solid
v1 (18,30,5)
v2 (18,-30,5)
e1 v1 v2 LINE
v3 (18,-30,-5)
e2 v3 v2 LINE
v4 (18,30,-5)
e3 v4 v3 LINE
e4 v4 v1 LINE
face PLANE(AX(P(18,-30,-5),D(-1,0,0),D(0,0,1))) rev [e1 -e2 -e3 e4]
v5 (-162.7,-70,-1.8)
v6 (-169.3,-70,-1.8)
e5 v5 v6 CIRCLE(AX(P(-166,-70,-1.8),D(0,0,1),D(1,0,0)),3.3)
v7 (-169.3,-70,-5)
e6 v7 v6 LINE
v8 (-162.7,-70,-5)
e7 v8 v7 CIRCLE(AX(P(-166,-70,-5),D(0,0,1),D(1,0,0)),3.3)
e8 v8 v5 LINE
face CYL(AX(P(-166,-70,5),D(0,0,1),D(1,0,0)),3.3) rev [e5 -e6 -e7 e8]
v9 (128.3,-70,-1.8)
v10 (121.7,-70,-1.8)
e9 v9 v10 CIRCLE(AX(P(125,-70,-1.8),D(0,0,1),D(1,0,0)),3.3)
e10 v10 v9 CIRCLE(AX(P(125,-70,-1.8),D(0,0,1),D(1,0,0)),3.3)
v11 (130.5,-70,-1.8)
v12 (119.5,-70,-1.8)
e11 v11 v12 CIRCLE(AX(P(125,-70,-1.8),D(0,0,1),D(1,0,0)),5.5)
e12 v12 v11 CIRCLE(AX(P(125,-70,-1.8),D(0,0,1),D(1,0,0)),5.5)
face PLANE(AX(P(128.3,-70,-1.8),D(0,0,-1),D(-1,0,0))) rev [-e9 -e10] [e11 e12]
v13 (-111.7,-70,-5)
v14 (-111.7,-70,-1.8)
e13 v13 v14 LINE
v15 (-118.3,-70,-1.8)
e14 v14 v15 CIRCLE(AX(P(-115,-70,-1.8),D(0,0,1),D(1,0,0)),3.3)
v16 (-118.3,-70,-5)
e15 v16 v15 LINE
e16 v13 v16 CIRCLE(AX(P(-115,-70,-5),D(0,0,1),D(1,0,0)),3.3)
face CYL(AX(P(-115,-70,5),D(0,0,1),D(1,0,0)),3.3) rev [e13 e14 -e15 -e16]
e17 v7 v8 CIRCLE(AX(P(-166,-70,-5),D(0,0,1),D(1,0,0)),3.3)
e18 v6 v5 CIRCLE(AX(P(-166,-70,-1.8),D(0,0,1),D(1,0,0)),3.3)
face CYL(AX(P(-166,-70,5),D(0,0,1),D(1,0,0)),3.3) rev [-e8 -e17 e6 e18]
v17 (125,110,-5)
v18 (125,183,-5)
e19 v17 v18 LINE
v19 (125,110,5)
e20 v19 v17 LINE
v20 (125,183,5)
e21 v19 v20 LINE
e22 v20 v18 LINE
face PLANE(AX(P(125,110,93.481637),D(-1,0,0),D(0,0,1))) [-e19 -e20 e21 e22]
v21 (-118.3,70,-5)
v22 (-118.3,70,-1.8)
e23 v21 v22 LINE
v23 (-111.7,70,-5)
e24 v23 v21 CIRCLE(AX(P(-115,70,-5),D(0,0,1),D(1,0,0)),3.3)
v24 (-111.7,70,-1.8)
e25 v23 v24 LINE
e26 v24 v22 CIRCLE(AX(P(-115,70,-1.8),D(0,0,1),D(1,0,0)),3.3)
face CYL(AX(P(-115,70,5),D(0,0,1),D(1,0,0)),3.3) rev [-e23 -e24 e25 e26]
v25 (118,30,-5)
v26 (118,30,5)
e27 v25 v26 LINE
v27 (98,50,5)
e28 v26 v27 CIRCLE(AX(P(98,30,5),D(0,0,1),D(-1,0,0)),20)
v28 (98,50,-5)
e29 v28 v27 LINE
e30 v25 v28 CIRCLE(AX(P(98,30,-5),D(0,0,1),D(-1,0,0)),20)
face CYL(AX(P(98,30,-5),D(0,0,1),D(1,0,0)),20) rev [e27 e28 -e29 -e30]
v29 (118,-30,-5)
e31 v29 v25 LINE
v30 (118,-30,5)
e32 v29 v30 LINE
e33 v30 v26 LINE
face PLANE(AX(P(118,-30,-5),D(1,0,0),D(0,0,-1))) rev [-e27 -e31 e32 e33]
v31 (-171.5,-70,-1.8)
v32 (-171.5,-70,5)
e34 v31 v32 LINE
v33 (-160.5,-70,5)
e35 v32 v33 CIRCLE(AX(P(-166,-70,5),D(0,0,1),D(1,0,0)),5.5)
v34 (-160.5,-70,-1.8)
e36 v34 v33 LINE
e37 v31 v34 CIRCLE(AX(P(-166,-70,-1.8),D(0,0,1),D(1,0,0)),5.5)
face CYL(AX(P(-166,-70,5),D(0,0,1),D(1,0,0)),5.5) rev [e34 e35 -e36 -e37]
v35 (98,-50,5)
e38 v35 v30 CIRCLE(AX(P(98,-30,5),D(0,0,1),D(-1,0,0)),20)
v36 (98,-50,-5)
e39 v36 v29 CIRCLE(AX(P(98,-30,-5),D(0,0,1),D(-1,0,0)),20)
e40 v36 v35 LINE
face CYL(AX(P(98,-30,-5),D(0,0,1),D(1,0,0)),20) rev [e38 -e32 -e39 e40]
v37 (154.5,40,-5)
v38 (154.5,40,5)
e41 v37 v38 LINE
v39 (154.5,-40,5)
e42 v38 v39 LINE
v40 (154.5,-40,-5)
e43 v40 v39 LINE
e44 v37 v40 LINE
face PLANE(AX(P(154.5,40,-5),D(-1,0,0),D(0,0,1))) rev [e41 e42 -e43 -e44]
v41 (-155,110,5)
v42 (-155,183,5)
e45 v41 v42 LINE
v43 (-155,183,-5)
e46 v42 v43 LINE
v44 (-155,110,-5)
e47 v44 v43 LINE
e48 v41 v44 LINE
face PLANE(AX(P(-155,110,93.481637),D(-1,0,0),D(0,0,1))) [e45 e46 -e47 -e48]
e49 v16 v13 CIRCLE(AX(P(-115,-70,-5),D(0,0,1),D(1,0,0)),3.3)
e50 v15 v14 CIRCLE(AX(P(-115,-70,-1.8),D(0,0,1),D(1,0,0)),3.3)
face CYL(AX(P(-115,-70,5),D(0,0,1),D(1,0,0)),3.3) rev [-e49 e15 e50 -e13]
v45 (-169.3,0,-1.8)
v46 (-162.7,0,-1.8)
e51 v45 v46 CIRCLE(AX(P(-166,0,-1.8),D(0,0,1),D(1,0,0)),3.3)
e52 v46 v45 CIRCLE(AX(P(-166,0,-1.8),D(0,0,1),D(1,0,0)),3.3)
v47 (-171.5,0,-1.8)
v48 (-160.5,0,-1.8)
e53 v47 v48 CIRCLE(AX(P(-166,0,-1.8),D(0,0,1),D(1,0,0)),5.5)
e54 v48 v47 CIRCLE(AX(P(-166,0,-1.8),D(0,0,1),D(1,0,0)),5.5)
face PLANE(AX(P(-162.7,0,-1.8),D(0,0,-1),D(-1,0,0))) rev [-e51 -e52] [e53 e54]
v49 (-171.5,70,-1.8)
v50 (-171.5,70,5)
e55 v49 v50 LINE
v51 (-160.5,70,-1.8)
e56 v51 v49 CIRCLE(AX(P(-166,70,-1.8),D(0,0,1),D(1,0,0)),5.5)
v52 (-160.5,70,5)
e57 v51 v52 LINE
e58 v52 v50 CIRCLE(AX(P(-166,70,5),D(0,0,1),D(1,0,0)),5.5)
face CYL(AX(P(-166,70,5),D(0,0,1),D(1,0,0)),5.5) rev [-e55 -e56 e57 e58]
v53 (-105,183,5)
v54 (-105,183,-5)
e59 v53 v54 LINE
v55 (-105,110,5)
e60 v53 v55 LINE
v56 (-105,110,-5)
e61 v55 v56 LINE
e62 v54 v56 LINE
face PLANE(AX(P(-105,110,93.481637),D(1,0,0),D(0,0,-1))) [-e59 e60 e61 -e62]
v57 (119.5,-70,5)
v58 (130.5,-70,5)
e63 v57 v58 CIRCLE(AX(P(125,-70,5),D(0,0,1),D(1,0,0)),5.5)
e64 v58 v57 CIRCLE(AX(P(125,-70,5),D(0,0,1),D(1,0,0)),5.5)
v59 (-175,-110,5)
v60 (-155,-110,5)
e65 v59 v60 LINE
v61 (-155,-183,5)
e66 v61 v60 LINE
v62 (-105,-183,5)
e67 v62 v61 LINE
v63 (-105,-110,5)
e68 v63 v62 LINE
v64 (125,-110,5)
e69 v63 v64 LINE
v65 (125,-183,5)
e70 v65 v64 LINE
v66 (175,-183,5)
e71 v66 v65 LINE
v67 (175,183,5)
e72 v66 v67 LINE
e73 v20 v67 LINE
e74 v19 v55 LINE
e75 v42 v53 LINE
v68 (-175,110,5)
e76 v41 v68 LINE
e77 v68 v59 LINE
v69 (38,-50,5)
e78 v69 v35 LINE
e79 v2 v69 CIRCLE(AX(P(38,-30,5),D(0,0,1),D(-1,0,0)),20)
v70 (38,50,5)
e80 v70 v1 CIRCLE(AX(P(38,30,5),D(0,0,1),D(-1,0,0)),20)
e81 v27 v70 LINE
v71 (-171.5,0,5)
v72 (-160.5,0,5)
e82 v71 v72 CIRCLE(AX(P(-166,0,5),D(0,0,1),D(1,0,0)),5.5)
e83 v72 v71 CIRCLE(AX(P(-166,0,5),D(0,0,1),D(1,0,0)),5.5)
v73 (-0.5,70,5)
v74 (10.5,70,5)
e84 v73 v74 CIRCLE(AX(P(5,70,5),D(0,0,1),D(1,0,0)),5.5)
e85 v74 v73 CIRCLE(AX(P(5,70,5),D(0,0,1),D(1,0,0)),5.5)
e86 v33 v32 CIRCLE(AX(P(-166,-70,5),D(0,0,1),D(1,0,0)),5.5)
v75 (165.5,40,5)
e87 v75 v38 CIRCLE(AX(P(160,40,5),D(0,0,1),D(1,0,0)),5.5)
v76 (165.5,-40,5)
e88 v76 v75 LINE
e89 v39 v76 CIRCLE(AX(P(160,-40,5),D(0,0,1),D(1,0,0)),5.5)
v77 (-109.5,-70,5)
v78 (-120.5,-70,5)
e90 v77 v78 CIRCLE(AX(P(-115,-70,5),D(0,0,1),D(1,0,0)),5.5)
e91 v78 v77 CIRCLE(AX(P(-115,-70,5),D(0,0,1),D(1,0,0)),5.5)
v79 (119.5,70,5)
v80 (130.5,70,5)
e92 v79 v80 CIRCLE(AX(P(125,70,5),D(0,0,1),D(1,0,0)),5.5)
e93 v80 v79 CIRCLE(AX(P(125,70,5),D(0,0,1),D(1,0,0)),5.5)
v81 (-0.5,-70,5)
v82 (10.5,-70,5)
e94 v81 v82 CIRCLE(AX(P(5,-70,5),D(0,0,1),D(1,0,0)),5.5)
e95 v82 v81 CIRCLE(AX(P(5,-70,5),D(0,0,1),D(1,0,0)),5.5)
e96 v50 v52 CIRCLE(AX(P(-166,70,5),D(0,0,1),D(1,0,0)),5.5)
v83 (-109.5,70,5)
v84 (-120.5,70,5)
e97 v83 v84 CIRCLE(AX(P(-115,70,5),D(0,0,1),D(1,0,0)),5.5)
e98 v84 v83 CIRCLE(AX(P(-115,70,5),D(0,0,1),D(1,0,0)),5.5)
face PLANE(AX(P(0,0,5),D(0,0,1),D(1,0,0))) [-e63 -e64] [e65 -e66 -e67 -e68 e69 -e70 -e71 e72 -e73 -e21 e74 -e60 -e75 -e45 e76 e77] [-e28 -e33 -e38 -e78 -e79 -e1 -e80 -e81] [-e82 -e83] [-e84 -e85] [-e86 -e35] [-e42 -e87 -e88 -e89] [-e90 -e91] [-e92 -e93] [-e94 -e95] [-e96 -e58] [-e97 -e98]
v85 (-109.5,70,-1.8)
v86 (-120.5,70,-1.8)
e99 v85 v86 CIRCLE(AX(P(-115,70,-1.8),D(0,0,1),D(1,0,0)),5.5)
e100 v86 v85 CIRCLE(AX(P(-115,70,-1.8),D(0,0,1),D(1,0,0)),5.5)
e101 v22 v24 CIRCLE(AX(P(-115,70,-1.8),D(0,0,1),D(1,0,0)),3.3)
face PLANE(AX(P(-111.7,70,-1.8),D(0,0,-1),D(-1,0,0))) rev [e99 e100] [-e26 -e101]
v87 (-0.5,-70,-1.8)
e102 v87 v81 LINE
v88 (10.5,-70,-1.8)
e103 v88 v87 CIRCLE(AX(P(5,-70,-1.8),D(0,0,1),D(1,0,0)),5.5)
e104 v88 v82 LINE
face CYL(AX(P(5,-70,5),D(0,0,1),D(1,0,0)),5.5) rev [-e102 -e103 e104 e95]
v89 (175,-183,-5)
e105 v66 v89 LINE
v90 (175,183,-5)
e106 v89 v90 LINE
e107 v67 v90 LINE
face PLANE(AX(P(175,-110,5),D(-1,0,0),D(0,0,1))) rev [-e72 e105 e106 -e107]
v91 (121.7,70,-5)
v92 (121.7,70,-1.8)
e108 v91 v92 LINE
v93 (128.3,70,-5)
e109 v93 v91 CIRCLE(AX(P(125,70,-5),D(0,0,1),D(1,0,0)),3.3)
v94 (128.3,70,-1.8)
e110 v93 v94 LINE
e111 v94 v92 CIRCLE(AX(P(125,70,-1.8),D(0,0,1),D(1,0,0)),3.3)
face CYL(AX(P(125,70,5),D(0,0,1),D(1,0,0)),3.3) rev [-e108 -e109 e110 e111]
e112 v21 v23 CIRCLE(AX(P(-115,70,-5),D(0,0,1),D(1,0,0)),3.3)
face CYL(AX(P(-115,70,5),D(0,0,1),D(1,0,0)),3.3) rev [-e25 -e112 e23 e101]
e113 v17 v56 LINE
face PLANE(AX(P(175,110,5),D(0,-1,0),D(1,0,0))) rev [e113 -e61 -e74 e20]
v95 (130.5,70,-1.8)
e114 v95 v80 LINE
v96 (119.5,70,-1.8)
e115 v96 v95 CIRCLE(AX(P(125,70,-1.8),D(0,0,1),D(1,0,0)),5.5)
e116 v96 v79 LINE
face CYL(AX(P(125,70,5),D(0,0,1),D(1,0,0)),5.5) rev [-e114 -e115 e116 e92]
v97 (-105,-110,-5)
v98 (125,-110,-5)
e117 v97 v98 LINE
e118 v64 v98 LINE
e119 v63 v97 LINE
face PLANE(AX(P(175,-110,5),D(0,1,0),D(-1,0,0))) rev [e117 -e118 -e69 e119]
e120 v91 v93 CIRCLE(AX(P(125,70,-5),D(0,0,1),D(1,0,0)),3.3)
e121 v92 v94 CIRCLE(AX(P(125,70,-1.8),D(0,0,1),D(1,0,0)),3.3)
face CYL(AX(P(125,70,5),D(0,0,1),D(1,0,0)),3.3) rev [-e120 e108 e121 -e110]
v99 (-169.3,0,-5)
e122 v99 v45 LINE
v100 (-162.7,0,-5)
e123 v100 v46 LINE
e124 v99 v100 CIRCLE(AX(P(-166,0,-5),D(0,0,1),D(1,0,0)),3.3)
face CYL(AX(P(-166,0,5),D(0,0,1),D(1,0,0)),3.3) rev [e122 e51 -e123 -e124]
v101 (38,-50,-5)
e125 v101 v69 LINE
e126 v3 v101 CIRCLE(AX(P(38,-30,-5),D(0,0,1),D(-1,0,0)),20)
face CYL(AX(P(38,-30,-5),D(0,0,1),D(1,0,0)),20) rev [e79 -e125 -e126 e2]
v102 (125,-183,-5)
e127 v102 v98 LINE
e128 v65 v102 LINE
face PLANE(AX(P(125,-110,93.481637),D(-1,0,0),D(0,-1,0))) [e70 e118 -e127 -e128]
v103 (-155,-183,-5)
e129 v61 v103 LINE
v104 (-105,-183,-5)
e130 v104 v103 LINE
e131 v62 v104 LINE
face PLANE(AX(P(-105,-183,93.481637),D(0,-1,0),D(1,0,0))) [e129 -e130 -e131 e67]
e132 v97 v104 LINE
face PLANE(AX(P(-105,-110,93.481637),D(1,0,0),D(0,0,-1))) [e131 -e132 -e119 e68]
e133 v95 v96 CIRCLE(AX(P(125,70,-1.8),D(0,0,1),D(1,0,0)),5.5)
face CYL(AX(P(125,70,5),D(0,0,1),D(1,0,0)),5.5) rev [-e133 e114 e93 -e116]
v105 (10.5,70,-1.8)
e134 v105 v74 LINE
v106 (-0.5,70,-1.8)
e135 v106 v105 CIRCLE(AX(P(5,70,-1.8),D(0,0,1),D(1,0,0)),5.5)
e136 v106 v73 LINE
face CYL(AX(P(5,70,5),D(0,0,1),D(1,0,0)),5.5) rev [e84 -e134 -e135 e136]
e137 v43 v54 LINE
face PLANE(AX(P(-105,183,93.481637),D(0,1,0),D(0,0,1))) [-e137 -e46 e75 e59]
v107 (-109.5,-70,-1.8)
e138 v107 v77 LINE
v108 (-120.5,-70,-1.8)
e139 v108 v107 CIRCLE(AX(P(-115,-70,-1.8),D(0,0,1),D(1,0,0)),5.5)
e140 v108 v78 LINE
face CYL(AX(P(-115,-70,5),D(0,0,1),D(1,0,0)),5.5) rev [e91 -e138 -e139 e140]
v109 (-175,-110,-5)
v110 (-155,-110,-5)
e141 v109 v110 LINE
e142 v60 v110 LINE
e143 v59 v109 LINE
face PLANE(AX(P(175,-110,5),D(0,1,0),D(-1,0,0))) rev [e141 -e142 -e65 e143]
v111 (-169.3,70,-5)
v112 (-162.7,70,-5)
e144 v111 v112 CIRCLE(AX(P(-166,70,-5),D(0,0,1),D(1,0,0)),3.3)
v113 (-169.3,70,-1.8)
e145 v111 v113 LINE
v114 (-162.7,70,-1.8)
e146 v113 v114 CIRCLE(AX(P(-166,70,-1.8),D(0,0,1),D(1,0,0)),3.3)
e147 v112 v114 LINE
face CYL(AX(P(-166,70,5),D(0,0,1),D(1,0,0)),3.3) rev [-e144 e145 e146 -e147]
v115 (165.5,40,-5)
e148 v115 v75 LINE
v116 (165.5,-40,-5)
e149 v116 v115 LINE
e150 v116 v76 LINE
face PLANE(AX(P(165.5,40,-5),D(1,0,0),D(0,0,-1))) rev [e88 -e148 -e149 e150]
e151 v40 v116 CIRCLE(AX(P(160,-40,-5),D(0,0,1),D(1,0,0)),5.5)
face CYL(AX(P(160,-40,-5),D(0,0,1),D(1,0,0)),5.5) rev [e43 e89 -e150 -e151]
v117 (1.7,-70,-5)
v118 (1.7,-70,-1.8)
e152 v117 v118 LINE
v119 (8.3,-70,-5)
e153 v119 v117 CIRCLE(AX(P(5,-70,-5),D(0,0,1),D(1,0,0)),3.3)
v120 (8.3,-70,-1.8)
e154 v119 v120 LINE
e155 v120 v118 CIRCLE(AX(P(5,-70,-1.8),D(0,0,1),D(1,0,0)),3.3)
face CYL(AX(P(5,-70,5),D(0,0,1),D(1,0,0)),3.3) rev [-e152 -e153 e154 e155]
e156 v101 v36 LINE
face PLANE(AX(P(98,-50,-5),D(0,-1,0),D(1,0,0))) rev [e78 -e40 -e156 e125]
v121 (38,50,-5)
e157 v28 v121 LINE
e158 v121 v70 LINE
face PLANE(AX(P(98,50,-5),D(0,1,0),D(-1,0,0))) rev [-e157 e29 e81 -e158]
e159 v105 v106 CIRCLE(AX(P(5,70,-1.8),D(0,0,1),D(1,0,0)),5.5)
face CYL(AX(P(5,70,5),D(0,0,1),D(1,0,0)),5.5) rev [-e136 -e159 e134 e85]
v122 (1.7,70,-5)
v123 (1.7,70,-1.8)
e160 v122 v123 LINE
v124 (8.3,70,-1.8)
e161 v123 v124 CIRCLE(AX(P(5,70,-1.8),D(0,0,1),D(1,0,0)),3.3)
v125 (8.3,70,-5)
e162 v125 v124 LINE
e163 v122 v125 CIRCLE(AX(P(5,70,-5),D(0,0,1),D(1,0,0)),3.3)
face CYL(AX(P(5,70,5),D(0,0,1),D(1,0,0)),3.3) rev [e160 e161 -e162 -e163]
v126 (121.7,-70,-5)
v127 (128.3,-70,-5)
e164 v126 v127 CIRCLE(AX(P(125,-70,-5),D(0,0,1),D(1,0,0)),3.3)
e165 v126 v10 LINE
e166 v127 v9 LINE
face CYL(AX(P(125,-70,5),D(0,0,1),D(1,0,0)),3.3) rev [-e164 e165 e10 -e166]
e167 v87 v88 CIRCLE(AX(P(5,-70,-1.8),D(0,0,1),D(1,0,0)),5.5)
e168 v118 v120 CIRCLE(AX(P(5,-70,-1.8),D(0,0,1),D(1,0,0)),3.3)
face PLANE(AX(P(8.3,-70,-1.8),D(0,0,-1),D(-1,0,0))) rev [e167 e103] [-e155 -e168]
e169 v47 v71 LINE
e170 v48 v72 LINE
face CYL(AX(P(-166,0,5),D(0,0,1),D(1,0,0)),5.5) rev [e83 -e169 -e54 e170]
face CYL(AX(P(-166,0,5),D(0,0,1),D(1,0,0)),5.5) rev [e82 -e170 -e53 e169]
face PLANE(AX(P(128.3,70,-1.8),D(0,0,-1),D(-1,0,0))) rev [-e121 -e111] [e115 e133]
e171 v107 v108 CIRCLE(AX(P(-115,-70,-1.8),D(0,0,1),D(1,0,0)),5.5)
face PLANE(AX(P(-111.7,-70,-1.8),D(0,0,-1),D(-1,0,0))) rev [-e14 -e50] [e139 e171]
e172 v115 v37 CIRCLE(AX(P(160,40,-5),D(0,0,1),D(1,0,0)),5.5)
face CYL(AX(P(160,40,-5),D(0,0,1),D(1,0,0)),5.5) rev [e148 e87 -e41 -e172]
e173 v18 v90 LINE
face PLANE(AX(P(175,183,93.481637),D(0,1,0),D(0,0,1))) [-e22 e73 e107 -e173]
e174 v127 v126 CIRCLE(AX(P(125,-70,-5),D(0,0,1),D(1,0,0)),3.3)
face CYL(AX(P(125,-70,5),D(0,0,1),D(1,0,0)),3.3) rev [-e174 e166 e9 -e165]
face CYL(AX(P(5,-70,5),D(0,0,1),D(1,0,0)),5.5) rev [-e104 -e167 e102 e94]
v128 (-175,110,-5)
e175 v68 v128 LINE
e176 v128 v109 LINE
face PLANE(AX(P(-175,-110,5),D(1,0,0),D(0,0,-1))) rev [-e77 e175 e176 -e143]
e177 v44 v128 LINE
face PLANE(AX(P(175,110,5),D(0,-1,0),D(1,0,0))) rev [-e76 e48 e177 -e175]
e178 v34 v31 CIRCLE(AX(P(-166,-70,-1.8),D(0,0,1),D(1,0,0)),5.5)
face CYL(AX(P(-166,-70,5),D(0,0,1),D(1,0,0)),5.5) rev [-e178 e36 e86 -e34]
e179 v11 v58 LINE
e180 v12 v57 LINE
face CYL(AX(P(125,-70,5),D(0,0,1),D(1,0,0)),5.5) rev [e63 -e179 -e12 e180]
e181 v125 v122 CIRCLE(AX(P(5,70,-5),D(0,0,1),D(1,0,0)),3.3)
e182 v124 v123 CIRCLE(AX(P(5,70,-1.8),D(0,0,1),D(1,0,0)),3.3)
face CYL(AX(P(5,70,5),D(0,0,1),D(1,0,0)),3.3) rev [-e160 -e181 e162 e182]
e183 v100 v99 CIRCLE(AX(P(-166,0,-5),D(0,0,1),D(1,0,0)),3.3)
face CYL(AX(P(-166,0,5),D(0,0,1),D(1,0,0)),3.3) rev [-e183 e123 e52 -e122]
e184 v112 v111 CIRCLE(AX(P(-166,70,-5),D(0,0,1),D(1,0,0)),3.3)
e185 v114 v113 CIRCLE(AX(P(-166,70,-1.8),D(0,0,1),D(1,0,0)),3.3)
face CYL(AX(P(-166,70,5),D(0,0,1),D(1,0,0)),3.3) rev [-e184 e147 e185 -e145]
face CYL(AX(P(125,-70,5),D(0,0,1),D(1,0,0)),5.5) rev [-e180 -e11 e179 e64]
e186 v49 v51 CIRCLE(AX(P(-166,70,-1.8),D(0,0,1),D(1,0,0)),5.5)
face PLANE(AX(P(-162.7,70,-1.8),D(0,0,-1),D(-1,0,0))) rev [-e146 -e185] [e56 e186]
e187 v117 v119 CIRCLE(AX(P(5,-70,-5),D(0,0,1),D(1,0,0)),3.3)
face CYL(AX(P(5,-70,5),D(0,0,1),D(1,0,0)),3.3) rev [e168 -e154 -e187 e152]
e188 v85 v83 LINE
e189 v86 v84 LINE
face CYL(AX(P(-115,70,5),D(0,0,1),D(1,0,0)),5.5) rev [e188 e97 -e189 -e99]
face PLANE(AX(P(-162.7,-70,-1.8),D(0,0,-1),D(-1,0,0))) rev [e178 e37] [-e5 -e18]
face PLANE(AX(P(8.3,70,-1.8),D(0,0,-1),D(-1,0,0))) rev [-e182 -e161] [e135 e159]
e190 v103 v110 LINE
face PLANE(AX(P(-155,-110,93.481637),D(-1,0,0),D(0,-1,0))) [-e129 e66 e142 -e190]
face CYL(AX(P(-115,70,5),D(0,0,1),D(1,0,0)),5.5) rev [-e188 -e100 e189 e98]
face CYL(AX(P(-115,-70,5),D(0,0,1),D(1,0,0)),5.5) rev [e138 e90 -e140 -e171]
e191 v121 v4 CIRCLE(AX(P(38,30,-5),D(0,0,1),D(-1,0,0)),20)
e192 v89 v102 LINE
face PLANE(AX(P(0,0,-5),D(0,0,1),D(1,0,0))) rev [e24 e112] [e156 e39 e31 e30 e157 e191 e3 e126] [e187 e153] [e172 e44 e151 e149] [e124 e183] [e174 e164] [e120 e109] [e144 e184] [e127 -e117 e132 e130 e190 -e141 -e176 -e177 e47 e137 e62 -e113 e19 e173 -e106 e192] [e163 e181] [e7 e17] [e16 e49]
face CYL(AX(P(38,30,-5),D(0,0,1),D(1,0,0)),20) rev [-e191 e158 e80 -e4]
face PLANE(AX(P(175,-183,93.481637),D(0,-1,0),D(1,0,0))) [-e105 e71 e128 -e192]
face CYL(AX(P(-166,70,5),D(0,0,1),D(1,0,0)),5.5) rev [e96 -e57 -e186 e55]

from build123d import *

# Parameters (mm, degrees)
SKETCH_1_W                = 350
SKETCH_1_H                = 220
EXTRUDE_1_DEPTH           = 5
CUT_EXTRUDE_1_DEPTH       = 207.942020866
CUT_EXTRUDE_2_DEPTH       = 207.942020866
HOLE_WIZARD_1_D           = 6.6
HOLE_WIZARD_1_DEPTH       = 15
HOLE_WIZARD_1_CBORE_D     = 11
HOLE_WIZARD_1_CBORE_DEPTH = 6.8
HOLE_WIZARD_1_TIP         = 1.982840043
SKETCH_8_W                = 50
SKETCH_8_H                = 73
EXTRUDE_2_DEPTH           = 10
PATTERN_LINEAR_1_COUNT    = 2
PATTERN_LINEAR_1_PITCH    = 280


with BuildPart() as part:
    # 草图1 → 凸台-拉伸1 (new, symmetric)
    with BuildSketch(Plane.XY):
        Rectangle(SKETCH_1_W, SKETCH_1_H)
    extrude(amount=EXTRUDE_1_DEPTH, both=True)

    # 草图2 → 切除-拉伸1 (cut, through all)
    with BuildSketch(Plane.XY.offset(5)):
        with BuildLine():
            Line((-208, 40), (-208, -40))
            ThreePointArc((-208, -40), (-213.5, -45.5), (-219, -40))
            Line((-219, -40), (-219, 40))
            ThreePointArc((-219, 40), (-213.5, 45.5), (-208, 40))
        make_face()
        with BuildLine():
            Line((165.5, 40), (165.5, -40))
            ThreePointArc((165.5, -40), (160, -45.5), (154.5, -40))
            Line((154.5, -40), (154.5, 40))
            ThreePointArc((154.5, 40), (160, 45.5), (165.5, 40))
        make_face()
    extrude(amount=-CUT_EXTRUDE_1_DEPTH, mode=Mode.SUBTRACT)

    # 草图6 → 切除-拉伸2 (cut, through all)
    with BuildSketch(Plane.XY.offset(5)):
        with BuildLine():
            Line((98, -50), (38, -50))
            ThreePointArc((38, -50), (23.857864376, -44.142135624), (18, -30))
            Line((18, -30), (18, 30))
            ThreePointArc((18, 30), (23.857864376, 44.142135624), (38, 50))
            Line((38, 50), (98, 50))
            ThreePointArc((98, 50), (112.142135624, 44.142135624), (118, 30))
            Line((118, 30), (118, -30))
            ThreePointArc((118, -30), (112.142135624, -44.142135624), (98, -50))
        make_face()
    extrude(amount=-CUT_EXTRUDE_2_DEPTH, mode=Mode.SUBTRACT)

    # 打孔尺寸(%根据)内六角圆柱头螺钉的类型1
    with Locations(Plane(origin=(-115, 70, 5), x_dir=(1, 0, 0), z_dir=(0, 0, 1))):
        with Locations((0, 0), (0, -140), (-51, 0), (-51, -140), (-51, -70), (120, 0), (240, 0), (240, -140), (120, -140)):
            CounterBoreHole(HOLE_WIZARD_1_D / 2, HOLE_WIZARD_1_CBORE_D / 2, HOLE_WIZARD_1_CBORE_DEPTH, depth=HOLE_WIZARD_1_DEPTH)
            with Locations((0, 0, -(HOLE_WIZARD_1_DEPTH + HOLE_WIZARD_1_TIP / 2))):  # 118° drill point
                Cone(0, HOLE_WIZARD_1_D / 2, HOLE_WIZARD_1_TIP, mode=Mode.SUBTRACT)

    # 草图8 → 凸台-拉伸2 (add)
    with BuildSketch(Plane(origin=(0, 0, -5), x_dir=(-1, 0, 0), z_dir=(0, 0, -1))):
        with Locations((-150, 146.5)):
            Rectangle(SKETCH_8_W, SKETCH_8_H)
        with Locations((-150, -146.5)):
            Rectangle(SKETCH_8_W, SKETCH_8_H)
    extrude_2 = extrude(amount=-EXTRUDE_2_DEPTH)

    # 阵列(线性)1: 凸台-拉伸2 ×2
    with Locations(*[(-i * PATTERN_LINEAR_1_PITCH, 0, 0) for i in range(1, PATTERN_LINEAR_1_COUNT)]):
        add(extrude_2)


solid = part.part
